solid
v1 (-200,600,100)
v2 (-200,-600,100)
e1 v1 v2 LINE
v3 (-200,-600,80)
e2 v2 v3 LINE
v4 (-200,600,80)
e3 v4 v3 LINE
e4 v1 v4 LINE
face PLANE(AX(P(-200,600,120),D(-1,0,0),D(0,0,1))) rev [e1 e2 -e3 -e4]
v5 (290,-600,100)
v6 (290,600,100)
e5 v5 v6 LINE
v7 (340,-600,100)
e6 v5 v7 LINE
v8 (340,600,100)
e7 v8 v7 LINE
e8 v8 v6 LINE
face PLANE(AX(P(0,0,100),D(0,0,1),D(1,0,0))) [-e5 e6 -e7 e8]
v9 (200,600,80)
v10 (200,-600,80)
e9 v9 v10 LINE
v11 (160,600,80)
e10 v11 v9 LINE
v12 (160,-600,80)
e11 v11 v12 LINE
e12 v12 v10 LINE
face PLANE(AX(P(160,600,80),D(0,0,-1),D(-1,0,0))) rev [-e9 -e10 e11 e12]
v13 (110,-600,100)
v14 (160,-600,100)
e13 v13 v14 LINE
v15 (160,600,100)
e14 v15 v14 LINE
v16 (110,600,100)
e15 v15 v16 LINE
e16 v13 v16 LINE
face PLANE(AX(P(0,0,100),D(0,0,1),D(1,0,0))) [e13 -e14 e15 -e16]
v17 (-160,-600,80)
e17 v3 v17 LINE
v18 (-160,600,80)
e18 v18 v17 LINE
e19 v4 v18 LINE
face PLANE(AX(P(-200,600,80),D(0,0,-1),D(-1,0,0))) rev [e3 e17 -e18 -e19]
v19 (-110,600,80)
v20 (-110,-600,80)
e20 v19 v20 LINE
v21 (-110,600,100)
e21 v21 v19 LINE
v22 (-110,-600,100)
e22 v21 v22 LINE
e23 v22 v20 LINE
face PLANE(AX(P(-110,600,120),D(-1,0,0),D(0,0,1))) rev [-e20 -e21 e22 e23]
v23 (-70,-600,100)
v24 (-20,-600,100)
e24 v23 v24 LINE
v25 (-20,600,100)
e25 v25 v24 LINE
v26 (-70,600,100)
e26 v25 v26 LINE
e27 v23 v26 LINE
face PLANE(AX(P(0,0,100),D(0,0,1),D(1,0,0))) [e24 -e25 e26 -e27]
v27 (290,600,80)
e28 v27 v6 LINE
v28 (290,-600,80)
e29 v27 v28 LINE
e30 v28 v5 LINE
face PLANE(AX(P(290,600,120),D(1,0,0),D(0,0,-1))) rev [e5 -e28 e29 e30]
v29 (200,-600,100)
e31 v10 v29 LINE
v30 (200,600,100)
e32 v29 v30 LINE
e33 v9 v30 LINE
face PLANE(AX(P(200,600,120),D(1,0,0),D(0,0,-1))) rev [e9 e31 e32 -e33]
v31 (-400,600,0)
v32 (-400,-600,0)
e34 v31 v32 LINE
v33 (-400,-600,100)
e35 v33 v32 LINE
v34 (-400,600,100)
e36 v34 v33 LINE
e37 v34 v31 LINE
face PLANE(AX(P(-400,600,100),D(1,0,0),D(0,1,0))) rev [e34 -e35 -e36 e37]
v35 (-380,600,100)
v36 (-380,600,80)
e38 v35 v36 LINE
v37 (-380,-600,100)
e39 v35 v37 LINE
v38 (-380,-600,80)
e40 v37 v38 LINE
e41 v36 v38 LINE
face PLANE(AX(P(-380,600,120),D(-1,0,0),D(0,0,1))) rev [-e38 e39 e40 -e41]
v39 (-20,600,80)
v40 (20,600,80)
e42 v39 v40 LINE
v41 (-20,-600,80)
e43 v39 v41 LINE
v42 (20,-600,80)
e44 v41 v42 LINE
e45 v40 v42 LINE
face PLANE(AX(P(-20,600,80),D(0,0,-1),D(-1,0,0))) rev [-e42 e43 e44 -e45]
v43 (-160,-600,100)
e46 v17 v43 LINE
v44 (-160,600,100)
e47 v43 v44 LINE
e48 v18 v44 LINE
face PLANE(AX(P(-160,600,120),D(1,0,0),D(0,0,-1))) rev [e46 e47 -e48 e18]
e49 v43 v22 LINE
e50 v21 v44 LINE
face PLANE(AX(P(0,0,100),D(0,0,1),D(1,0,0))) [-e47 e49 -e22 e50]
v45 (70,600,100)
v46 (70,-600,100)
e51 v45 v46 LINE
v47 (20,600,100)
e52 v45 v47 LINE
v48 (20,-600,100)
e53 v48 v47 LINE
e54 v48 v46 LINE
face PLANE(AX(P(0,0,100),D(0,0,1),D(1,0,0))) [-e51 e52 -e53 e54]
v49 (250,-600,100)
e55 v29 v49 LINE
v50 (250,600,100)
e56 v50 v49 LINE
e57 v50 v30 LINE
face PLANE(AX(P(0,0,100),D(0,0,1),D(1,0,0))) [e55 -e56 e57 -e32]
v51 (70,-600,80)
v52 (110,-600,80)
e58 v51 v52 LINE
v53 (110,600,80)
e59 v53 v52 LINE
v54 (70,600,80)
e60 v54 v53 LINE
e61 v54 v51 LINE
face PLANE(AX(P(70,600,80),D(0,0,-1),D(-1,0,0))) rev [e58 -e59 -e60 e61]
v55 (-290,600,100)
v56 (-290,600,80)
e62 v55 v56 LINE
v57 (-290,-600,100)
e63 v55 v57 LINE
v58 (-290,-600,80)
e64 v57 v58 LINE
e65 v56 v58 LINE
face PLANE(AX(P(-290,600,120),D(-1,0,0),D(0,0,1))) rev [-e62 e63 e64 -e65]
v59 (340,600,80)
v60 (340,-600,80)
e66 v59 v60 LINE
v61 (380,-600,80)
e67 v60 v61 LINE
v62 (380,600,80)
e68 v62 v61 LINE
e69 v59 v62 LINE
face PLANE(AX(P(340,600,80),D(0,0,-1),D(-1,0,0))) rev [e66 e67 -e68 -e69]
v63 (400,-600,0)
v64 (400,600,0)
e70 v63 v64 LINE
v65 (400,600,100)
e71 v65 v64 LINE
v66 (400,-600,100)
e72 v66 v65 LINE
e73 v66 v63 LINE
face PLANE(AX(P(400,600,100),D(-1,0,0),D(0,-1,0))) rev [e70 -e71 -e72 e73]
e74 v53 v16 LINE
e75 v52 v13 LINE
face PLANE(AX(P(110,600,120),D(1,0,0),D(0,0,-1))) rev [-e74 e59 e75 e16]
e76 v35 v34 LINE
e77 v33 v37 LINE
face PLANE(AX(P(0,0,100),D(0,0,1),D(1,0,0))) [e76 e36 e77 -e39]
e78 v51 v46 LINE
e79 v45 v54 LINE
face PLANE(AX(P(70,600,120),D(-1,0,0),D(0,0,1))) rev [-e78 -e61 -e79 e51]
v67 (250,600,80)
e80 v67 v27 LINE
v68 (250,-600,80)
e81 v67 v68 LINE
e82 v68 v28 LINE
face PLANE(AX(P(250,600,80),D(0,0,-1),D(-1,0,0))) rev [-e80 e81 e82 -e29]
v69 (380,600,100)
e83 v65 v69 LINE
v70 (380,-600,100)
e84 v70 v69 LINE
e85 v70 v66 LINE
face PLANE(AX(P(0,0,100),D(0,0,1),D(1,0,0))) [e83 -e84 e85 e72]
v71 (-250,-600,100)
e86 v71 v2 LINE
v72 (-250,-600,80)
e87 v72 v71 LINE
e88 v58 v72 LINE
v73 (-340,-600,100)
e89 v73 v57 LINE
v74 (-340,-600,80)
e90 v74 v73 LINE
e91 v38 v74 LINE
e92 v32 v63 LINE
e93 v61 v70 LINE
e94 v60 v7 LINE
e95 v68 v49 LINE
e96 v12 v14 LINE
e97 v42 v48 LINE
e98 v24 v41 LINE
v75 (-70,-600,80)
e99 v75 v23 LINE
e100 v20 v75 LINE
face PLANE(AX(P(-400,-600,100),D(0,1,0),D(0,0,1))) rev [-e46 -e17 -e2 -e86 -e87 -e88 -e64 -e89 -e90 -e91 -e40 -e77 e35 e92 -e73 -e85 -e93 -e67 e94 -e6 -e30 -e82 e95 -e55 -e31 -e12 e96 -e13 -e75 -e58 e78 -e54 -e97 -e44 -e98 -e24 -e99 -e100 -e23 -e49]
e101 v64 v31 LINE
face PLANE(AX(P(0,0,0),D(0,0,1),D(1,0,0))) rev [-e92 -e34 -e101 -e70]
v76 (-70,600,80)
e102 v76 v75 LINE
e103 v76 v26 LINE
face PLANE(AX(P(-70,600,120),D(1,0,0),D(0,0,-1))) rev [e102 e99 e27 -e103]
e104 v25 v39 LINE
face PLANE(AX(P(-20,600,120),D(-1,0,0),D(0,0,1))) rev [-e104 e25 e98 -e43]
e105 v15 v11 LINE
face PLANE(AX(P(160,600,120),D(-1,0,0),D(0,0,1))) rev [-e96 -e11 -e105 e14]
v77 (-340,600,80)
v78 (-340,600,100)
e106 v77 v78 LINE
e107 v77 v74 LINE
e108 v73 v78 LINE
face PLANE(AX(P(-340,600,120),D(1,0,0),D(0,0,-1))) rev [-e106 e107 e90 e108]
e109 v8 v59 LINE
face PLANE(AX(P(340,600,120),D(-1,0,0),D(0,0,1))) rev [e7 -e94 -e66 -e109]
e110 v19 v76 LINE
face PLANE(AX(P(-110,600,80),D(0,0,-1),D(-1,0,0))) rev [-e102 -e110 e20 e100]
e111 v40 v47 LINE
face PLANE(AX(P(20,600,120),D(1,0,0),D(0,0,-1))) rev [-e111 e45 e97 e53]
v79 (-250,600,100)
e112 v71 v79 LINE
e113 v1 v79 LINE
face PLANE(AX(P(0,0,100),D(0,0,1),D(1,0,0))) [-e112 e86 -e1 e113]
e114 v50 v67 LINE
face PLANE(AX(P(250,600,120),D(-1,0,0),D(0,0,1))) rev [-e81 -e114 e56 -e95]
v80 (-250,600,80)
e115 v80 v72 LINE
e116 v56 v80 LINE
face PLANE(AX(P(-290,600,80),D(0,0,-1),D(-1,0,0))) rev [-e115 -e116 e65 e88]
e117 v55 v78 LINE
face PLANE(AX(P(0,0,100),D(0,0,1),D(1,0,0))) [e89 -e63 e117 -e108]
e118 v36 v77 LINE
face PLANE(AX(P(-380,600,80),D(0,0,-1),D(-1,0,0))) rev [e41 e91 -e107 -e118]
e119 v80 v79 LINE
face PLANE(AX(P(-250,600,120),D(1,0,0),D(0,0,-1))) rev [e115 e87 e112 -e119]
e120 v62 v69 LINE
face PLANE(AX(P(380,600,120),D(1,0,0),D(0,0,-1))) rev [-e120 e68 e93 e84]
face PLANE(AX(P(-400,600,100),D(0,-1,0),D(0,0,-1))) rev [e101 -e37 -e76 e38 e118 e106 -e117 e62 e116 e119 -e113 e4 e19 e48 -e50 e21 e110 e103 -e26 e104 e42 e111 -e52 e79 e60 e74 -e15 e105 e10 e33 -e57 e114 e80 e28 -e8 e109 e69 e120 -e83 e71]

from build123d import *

# Parameters (mm, degrees)
SKETCH1_W           = 800
SKETCH1_H           = 1200
BOSS_EXTRUDE1_DEPTH = 100
SKETCH2_W           = 40
SKETCH2_H           = 40
CUT_EXTRUDE1_DEPTH  = 1269.857754045
LPATTERN1_COUNT     = 5
LPATTERN1_PITCH     = 90
LPATTERN1_COL_COUNT = 5
LPATTERN1_COL_PITCH = 90


with BuildPart() as part:
    # Sketch1 → Boss-Extrude1 (new body)
    with BuildSketch(Plane.XY):
        Rectangle(SKETCH1_W, SKETCH1_H)
    extrude(amount=BOSS_EXTRUDE1_DEPTH)

    # Sketch2 → Cut-Extrude1 (cut, through all)
    with BuildSketch(Plane.XZ.offset(600)):
        with Locations((0, 100)):
            Rectangle(SKETCH2_W, SKETCH2_H)
    cut_extrude1 = extrude(amount=-CUT_EXTRUDE1_DEPTH, mode=Mode.SUBTRACT)

    # LPattern1: Cut-Extrude1 ×5
    with Locations(*[(i * LPATTERN1_PITCH, 0, 0) for i in range(1, LPATTERN1_COUNT)]):
        add(cut_extrude1, mode=Mode.SUBTRACT)

    # LPattern1 col: Cut-Extrude1 ×5
    with Locations(*[(-i * LPATTERN1_COL_PITCH, 0, 0) for i in range(1, LPATTERN1_COL_COUNT)]):
        add(cut_extrude1, mode=Mode.SUBTRACT)


solid = part.part
